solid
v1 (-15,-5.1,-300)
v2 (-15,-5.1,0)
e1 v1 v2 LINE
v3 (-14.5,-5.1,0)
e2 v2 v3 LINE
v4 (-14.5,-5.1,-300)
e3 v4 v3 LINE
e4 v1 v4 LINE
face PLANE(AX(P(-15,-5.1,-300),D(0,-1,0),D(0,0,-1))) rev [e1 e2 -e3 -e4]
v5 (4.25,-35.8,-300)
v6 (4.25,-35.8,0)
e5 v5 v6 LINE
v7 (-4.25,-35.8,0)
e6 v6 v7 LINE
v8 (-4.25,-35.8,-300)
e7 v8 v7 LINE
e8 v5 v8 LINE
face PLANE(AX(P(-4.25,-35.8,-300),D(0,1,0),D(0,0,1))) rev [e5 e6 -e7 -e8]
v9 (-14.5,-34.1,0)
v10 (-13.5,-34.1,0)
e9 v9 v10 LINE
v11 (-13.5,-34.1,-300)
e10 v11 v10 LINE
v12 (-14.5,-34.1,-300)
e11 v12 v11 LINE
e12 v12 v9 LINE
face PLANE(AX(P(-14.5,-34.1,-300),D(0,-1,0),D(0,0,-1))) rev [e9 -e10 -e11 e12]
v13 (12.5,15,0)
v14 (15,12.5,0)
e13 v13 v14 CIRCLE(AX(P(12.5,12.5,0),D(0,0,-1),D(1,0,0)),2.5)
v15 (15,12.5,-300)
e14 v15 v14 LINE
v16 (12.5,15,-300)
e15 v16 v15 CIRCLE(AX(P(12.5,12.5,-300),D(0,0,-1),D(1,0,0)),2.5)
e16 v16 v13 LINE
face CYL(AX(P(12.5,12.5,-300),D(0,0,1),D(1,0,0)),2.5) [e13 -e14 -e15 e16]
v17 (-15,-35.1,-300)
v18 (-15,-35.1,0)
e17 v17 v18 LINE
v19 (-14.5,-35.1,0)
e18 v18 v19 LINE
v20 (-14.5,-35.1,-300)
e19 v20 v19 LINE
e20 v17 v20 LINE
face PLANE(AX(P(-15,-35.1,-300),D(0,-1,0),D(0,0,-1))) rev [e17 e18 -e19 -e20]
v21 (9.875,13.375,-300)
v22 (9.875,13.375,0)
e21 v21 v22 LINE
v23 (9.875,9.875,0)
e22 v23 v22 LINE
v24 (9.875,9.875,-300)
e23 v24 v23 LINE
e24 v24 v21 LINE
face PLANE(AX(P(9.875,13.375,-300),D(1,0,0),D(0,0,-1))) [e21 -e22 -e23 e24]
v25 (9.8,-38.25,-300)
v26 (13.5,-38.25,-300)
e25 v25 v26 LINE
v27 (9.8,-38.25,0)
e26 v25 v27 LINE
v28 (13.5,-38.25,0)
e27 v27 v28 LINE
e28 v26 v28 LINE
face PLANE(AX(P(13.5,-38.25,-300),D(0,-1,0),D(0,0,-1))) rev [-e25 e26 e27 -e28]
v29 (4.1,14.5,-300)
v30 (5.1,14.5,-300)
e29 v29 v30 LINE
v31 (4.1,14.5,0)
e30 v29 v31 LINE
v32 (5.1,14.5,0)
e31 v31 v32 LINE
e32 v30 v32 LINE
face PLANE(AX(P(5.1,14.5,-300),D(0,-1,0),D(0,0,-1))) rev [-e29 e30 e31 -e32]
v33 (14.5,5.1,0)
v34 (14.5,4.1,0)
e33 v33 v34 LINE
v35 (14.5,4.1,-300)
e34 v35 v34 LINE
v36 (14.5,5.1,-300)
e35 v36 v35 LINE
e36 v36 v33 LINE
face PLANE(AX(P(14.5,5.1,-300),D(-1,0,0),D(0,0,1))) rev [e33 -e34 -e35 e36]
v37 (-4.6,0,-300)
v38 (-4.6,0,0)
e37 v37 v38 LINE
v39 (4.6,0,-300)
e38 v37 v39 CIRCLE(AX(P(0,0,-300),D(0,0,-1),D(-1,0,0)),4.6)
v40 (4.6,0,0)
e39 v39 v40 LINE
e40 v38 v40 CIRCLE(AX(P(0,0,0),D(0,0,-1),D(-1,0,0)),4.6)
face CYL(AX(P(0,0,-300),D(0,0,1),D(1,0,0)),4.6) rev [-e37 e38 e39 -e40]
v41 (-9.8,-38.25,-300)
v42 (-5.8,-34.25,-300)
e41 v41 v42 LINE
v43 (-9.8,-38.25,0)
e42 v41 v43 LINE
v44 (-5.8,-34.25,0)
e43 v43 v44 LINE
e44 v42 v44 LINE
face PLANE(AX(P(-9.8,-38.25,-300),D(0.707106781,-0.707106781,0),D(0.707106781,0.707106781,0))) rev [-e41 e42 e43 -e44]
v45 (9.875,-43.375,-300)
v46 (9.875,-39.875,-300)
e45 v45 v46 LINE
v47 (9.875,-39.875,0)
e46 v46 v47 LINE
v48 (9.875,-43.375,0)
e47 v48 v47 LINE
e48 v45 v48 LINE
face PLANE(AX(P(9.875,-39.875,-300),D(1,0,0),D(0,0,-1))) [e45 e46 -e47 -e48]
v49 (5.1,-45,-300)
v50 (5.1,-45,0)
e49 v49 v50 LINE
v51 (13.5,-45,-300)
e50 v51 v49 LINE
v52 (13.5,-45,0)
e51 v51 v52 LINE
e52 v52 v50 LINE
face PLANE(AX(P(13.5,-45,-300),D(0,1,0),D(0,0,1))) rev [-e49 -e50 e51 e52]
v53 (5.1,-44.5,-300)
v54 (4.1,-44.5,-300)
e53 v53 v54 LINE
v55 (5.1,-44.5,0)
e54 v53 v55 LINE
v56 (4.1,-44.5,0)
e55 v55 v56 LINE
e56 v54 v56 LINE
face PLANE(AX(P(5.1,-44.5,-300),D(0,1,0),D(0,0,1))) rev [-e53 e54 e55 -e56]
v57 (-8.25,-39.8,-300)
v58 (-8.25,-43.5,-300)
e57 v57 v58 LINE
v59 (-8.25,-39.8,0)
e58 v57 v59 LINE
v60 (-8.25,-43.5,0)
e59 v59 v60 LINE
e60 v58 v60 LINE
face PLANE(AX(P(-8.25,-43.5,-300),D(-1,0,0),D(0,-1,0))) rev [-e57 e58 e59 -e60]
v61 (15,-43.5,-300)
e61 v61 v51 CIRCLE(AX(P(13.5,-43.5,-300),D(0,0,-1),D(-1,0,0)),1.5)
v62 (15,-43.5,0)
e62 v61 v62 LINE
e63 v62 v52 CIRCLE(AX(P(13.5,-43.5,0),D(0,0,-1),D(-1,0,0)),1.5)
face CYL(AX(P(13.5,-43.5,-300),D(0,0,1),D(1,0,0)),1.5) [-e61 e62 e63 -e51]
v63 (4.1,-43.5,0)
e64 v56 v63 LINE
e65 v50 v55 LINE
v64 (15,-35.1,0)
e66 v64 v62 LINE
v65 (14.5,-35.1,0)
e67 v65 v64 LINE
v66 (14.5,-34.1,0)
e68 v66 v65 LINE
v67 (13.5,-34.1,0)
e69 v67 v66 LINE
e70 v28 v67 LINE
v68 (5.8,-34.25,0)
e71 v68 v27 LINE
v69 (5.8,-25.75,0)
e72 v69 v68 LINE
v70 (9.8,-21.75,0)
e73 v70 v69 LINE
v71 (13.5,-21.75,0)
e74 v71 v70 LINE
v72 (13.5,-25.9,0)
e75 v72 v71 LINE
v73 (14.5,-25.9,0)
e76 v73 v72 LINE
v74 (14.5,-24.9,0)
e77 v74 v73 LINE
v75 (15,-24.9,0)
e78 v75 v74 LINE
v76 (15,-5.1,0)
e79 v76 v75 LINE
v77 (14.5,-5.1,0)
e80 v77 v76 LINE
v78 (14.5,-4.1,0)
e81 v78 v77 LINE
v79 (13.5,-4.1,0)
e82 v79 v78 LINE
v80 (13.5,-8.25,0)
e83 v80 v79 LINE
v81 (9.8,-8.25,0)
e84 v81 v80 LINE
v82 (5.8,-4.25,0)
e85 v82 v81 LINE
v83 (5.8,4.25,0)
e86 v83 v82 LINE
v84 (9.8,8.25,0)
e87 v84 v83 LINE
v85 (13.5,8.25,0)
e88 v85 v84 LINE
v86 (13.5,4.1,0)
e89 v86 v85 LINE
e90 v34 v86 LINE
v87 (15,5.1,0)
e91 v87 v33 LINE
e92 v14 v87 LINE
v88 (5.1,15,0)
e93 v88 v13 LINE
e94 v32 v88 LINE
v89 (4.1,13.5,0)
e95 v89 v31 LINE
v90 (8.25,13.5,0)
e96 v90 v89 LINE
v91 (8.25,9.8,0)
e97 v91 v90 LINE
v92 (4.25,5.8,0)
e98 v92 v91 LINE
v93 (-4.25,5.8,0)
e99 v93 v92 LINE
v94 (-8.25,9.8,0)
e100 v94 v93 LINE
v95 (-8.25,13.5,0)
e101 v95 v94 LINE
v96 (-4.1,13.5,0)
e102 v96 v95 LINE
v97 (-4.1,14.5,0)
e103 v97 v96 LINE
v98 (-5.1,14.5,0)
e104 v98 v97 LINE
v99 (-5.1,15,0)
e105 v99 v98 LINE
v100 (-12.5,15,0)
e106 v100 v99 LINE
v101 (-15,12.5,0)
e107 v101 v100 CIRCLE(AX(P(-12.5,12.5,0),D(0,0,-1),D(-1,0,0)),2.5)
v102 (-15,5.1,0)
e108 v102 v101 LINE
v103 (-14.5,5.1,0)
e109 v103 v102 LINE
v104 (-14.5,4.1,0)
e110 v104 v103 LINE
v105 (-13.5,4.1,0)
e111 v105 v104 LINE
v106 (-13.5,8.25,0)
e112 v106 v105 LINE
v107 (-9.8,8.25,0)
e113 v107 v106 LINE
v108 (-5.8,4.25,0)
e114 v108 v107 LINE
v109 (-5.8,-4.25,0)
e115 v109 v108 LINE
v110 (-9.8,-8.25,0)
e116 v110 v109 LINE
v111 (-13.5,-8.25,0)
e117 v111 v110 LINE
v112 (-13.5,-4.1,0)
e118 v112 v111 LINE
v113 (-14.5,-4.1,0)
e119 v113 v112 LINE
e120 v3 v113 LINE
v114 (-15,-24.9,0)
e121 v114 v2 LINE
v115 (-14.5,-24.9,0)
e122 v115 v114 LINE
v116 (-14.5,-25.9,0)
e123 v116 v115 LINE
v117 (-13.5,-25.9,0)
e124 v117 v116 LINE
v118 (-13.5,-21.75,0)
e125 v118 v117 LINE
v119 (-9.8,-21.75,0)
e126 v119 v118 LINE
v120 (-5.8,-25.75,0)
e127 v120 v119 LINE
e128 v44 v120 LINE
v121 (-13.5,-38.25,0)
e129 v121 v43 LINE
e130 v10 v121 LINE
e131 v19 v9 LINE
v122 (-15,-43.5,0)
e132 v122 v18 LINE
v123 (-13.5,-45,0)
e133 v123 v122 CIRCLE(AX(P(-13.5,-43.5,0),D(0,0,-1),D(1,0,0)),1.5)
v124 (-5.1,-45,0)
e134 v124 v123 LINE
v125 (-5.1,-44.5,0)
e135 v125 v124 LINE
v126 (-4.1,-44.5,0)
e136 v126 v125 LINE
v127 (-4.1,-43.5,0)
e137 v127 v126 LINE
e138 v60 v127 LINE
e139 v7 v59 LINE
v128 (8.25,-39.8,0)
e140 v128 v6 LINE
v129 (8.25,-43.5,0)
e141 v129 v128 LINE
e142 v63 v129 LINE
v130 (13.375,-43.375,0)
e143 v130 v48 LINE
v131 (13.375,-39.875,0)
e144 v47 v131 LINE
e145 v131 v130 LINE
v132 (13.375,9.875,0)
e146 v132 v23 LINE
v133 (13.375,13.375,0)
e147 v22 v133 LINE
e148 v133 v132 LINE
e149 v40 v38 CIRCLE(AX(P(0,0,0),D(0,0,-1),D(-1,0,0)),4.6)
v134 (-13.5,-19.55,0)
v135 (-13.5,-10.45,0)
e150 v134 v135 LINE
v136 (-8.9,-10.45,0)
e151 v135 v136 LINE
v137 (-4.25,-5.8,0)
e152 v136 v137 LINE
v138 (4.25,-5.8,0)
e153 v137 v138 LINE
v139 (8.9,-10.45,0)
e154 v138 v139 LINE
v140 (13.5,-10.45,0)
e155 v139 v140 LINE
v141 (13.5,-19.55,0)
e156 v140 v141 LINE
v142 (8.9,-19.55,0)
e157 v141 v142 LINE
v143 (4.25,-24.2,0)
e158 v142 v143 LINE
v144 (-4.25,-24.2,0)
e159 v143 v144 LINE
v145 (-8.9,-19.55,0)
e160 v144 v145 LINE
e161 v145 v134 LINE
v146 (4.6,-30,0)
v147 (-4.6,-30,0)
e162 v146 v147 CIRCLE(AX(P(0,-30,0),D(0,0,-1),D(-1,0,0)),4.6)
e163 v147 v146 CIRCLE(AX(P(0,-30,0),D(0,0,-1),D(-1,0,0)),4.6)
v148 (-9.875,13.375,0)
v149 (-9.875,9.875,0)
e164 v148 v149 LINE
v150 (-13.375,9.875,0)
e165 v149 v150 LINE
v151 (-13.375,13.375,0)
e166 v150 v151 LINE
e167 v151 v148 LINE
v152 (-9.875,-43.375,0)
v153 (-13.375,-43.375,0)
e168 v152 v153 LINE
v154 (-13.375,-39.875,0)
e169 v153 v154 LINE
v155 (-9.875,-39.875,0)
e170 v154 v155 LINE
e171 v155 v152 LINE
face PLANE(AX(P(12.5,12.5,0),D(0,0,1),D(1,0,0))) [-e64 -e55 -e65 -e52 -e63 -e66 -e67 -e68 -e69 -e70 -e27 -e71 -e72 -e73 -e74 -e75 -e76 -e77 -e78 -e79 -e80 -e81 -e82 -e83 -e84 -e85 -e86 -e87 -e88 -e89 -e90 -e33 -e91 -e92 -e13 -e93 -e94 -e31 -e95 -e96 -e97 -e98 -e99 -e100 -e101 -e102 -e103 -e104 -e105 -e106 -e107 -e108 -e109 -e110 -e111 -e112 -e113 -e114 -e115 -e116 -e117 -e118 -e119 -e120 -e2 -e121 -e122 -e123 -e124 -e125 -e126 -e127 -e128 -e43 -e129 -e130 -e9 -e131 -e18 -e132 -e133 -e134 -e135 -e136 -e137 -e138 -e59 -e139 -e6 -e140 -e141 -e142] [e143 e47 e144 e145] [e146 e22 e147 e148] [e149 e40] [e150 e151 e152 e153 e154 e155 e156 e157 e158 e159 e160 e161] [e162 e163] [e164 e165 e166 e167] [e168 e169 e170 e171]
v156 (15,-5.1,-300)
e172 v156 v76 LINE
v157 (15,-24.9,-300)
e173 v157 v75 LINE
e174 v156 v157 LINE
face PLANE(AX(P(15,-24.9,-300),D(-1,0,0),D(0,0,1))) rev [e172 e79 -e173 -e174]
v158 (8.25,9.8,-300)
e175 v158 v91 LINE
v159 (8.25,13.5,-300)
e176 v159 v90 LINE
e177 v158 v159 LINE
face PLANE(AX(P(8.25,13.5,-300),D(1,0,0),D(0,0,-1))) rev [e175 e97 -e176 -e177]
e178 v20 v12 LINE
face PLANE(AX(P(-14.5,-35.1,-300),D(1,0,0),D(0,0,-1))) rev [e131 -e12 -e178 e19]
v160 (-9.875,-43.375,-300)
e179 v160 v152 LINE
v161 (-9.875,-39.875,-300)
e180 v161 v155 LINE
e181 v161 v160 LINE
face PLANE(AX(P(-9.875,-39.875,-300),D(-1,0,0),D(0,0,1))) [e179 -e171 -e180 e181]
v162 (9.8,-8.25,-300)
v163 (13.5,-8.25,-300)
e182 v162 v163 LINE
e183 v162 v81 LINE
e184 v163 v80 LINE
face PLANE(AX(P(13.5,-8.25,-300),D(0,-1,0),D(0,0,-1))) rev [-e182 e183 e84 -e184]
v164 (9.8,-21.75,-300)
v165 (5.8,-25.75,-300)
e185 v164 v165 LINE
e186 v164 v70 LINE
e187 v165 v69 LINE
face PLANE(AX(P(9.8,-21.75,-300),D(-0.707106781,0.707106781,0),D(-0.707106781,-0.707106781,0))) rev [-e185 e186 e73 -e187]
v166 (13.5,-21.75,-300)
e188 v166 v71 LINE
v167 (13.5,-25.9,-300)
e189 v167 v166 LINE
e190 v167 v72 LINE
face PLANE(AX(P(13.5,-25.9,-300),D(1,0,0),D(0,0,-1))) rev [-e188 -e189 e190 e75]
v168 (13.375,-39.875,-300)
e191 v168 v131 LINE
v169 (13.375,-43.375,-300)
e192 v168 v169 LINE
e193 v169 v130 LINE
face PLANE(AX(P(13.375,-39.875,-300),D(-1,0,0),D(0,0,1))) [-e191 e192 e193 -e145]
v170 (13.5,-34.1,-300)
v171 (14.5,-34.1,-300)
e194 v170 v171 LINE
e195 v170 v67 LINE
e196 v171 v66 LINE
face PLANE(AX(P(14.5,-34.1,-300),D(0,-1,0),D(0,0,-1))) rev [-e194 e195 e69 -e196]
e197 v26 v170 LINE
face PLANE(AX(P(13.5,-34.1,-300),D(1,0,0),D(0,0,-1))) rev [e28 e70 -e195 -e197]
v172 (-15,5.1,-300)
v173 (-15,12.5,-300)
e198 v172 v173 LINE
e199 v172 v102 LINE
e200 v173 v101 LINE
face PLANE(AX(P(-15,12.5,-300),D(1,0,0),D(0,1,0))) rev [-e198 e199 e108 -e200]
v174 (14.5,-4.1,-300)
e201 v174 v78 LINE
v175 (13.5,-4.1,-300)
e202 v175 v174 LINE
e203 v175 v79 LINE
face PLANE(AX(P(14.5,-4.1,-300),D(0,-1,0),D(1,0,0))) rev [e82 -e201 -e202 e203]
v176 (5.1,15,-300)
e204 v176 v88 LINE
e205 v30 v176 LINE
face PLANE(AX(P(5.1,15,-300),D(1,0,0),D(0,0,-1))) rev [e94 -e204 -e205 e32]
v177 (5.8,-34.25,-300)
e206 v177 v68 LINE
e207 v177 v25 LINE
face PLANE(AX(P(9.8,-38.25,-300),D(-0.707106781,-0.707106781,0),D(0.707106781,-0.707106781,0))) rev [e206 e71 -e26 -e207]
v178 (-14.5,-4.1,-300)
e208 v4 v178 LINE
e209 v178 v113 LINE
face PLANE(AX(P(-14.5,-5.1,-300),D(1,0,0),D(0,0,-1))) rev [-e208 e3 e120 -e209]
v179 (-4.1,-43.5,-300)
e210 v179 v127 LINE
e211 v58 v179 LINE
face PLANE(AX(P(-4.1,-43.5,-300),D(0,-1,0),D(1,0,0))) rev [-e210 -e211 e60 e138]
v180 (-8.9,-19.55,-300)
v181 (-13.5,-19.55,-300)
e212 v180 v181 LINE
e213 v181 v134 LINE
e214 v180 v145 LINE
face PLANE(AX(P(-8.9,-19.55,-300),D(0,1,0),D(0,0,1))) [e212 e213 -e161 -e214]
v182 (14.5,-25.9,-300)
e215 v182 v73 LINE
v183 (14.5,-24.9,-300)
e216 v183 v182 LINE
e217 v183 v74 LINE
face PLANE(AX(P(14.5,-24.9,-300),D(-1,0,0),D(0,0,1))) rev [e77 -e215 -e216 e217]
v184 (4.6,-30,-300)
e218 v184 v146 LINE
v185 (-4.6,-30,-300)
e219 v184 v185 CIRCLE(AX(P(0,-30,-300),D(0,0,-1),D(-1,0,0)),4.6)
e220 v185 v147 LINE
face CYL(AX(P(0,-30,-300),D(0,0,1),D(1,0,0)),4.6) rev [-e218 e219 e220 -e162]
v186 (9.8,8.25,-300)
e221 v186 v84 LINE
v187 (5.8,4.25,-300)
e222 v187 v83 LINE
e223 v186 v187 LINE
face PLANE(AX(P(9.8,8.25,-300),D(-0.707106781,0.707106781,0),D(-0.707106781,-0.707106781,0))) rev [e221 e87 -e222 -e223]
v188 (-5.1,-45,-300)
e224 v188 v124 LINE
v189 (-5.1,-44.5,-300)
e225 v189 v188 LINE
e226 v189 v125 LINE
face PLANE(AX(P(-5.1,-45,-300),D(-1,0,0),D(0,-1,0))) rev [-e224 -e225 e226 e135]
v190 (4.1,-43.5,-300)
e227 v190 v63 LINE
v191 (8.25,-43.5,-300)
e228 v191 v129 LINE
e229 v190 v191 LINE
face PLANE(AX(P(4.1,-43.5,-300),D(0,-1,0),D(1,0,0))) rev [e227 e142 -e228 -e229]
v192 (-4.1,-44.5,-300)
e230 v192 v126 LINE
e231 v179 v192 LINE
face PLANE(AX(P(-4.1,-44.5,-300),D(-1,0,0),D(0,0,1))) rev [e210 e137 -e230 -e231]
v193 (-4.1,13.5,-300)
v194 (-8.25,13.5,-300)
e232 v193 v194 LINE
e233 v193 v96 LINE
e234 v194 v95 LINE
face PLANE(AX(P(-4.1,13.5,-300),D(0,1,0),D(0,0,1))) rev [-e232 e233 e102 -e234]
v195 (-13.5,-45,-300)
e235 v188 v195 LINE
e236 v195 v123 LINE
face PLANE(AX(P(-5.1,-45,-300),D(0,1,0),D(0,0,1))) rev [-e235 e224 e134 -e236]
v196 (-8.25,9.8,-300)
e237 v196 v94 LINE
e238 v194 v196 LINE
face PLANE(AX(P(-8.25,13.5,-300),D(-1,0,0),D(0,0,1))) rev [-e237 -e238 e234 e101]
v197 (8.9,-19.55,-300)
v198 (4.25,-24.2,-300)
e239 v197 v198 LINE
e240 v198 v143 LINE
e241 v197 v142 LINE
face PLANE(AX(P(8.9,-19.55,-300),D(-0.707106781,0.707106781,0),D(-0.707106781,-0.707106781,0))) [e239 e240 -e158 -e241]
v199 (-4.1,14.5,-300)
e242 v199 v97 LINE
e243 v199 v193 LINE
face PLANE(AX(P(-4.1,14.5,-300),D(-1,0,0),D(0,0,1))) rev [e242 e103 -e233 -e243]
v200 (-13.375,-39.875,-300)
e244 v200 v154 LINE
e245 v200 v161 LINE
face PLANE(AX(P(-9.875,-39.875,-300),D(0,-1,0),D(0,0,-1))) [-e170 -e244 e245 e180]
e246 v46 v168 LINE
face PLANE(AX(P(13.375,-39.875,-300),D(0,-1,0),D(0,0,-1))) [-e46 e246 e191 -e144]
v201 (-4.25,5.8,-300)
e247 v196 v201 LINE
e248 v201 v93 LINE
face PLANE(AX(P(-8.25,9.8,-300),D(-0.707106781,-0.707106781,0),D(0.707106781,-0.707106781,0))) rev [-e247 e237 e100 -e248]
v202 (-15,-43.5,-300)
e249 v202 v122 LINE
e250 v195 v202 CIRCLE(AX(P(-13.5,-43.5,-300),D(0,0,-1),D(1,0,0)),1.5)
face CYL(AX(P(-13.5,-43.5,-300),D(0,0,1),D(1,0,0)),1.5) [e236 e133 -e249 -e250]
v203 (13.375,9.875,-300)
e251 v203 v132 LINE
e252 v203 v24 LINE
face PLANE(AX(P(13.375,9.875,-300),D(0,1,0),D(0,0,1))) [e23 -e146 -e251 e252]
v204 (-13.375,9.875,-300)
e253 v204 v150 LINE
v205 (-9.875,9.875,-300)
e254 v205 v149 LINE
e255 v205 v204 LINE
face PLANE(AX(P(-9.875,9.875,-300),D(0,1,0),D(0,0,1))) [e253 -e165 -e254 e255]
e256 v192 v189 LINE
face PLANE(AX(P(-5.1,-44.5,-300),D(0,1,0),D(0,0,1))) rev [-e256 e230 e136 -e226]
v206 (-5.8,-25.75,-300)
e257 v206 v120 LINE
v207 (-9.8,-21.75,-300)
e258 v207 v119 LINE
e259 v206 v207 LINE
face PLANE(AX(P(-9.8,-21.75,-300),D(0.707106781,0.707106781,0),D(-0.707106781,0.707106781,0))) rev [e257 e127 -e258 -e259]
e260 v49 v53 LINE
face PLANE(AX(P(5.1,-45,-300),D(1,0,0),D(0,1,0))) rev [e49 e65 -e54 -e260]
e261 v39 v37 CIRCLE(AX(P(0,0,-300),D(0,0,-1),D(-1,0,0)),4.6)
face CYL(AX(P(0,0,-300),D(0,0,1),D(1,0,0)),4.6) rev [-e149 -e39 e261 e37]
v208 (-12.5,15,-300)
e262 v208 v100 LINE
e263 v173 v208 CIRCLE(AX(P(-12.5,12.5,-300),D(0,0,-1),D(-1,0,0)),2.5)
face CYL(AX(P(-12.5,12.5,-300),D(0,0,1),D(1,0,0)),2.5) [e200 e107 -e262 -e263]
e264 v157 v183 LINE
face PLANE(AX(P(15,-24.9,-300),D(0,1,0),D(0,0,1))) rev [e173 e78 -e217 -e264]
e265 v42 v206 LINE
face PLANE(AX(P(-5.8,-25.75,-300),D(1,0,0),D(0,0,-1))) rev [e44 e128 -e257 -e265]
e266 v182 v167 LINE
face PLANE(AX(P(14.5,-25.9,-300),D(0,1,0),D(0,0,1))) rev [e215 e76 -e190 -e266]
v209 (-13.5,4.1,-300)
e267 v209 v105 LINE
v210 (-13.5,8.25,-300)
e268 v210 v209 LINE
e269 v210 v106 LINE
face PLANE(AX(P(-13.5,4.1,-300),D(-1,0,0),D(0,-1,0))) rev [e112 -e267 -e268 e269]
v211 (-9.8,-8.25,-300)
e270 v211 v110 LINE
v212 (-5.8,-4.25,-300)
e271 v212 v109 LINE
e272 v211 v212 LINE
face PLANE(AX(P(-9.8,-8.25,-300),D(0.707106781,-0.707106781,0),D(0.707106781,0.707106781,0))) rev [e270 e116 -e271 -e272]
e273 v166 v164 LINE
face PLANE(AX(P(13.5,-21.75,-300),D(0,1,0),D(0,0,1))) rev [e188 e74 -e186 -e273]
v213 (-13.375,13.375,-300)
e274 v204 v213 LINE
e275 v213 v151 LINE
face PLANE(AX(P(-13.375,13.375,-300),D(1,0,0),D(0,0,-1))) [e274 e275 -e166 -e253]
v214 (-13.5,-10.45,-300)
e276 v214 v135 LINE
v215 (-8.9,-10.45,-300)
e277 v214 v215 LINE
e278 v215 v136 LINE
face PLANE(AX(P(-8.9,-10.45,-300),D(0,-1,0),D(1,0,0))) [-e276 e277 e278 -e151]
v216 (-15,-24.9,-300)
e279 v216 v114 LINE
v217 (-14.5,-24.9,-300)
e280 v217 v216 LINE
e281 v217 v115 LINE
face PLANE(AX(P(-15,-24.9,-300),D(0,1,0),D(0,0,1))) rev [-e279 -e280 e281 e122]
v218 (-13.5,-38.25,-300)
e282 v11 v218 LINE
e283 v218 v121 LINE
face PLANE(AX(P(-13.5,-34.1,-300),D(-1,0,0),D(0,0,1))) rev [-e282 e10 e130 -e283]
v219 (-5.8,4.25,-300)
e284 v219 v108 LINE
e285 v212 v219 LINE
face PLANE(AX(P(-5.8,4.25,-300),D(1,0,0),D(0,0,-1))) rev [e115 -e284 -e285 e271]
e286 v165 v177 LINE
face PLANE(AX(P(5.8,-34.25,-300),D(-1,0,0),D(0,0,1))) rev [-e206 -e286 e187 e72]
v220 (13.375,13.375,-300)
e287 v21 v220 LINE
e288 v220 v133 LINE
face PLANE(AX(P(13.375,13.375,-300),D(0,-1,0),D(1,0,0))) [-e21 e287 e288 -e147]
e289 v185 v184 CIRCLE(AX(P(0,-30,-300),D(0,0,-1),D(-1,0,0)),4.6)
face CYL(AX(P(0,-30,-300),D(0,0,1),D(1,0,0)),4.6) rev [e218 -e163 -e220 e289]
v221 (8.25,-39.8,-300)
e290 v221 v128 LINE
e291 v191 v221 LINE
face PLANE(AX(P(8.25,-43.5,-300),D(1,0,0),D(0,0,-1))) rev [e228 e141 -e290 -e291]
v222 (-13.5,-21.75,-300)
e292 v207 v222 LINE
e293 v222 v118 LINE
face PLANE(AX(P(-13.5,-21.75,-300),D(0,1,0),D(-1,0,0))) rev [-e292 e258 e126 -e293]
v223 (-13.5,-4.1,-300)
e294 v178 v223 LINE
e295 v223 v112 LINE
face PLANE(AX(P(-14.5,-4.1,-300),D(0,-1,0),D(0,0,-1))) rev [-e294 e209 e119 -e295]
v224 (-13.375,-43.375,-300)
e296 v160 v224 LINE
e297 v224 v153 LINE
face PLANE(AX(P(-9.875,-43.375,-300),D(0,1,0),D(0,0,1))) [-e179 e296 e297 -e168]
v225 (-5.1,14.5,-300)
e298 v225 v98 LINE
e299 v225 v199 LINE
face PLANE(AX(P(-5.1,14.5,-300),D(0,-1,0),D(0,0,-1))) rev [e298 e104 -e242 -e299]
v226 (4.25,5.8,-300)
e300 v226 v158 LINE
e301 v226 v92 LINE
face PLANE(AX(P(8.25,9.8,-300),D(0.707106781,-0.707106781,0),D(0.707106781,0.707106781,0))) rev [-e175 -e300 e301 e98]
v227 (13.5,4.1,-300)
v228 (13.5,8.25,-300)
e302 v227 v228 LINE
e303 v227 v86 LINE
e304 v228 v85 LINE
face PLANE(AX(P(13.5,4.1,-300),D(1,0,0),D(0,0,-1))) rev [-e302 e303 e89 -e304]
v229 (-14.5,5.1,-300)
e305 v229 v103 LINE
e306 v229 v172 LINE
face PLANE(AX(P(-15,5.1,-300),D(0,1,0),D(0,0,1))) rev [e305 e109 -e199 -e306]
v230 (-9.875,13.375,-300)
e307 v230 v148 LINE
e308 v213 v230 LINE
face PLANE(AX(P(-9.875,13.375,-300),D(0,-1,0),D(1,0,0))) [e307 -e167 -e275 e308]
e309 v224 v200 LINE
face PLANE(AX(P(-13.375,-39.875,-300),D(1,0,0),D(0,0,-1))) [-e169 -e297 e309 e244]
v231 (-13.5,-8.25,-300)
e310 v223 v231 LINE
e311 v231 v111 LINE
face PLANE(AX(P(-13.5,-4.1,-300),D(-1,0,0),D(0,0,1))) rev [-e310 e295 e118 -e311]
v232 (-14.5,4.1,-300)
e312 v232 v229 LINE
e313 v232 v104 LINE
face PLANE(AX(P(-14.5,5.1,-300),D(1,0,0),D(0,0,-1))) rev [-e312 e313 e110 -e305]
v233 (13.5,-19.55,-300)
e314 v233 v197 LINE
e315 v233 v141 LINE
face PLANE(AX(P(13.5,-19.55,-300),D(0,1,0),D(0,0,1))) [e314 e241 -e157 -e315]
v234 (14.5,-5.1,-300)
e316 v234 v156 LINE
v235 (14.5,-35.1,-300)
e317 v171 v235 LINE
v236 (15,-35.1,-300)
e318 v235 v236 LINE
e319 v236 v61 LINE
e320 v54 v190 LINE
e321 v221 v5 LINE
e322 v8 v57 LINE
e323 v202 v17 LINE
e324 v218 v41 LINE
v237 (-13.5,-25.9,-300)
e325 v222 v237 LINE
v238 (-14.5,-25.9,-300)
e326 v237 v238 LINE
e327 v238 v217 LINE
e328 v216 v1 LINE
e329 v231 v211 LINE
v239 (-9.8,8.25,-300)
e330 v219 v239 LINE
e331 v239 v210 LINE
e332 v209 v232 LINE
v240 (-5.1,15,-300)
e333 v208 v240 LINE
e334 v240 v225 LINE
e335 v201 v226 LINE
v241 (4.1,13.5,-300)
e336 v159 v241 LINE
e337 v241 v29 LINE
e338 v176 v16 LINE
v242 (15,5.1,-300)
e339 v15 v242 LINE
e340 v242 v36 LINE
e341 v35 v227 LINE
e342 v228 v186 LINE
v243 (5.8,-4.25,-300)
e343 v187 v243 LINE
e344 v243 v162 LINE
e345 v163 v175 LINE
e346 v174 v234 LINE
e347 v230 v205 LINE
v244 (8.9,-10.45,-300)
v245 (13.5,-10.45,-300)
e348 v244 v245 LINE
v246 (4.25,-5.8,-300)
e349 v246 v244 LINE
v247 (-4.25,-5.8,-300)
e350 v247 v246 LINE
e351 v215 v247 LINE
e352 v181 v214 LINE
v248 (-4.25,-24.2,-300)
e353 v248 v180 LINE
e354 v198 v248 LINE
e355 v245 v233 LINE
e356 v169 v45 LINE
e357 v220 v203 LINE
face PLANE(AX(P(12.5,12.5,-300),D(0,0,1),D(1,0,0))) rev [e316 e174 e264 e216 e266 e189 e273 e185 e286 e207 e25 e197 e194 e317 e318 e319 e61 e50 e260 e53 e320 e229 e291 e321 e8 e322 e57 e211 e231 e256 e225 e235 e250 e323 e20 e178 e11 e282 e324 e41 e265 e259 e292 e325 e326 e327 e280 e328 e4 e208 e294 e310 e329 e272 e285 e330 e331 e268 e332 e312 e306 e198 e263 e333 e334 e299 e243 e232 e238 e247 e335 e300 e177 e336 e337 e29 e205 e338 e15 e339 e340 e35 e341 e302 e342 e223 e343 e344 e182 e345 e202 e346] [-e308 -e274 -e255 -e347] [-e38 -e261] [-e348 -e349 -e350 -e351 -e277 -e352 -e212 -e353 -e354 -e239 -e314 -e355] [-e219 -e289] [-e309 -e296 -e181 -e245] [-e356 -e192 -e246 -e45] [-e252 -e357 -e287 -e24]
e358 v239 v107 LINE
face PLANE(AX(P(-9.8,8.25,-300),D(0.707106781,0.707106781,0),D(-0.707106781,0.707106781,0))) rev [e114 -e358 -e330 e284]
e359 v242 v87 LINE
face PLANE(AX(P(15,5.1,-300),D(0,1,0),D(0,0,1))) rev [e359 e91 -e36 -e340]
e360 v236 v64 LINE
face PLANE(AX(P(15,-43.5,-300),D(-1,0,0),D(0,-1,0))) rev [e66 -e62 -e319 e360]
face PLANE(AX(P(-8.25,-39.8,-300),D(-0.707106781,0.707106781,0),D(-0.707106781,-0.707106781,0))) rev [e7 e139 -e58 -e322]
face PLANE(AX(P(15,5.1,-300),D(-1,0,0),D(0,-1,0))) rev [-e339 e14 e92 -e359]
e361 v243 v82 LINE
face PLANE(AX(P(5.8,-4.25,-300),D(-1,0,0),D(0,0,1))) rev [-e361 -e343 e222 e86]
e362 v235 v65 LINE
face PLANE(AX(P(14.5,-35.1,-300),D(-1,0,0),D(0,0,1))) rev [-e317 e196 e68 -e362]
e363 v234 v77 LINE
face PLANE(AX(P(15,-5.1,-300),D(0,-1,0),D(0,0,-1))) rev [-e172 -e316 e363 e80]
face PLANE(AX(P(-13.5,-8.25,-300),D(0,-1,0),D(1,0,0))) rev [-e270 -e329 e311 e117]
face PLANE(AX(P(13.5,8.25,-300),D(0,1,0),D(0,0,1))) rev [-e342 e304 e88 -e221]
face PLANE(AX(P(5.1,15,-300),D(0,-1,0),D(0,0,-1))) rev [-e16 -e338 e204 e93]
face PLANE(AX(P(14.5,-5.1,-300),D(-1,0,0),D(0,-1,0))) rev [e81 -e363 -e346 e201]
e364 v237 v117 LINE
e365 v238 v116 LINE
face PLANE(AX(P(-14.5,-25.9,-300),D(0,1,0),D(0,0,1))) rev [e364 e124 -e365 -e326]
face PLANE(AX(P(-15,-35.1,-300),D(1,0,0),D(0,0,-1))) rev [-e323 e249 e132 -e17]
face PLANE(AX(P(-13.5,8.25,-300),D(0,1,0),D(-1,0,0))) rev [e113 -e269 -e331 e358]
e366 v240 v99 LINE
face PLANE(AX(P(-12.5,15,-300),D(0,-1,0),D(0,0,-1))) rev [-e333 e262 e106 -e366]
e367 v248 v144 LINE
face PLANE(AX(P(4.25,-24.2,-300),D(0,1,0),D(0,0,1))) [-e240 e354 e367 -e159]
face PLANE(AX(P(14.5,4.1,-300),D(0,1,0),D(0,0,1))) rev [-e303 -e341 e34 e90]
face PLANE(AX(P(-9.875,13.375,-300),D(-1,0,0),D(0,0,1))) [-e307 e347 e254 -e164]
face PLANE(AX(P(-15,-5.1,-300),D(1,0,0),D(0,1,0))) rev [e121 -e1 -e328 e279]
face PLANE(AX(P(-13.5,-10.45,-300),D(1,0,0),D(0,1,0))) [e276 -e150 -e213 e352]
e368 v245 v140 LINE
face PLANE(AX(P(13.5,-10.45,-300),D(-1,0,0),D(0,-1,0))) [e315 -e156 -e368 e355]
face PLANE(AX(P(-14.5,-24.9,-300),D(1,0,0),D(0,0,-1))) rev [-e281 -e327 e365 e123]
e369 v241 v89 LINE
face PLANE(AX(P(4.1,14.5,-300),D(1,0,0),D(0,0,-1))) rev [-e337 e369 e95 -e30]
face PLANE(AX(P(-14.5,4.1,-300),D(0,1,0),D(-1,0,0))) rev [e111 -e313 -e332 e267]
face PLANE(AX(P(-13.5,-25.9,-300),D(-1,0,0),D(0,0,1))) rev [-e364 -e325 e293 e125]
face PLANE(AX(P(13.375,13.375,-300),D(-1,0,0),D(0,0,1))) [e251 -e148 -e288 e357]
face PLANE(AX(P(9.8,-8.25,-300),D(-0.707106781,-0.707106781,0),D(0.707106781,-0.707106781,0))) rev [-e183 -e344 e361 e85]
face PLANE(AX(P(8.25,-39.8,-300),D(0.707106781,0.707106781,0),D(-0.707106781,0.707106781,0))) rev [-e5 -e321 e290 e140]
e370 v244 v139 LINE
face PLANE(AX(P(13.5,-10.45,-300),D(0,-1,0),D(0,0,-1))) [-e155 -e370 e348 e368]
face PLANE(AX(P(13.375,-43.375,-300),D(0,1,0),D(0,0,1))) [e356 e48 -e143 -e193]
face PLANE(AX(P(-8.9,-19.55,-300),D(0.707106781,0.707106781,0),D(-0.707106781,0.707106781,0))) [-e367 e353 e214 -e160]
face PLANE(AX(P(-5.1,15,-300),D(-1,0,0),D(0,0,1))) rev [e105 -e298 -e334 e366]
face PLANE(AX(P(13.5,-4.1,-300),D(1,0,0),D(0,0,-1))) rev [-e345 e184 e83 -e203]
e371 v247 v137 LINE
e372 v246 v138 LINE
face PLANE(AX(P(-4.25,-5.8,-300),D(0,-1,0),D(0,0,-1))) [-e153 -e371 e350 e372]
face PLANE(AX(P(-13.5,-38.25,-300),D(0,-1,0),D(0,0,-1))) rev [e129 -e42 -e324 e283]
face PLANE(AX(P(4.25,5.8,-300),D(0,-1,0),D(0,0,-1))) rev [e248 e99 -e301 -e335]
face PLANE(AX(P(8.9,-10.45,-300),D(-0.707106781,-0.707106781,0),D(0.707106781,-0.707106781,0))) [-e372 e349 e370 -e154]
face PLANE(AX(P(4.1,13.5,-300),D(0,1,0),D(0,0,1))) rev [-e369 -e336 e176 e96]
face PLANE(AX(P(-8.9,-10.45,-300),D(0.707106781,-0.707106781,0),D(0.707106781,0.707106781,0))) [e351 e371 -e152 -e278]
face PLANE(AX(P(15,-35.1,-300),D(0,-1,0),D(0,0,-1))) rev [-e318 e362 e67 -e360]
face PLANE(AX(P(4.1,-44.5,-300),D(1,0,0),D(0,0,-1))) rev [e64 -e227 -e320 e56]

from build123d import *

# Parameters (mm, degrees)
SKETCH1_R                 = 4.6
SKETCH1_W                 = 3.5
SKETCH1_H                 = 3.5
F_30_X_60L_X_R2_5_1_DEPTH = 300


with BuildPart() as part:
    # Sketch1 → 铝型材 30 X 60L X R2.5(1) (new body)
    with BuildSketch(Plane(origin=(0, 0, 0), x_dir=(-1, 0, 0), z_dir=(0, 0, -1))):
        with BuildLine():
            Line((-5.1, 15), (-5.1, 14.5))
            Line((-5.1, 14.5), (-4.1, 14.5))
            Line((-4.1, 14.5), (-4.1, 13.5))
            Line((-4.1, 13.5), (-8.25, 13.5))
            Line((-8.25, 13.5), (-8.25, 9.8))
            Line((-8.25, 9.8), (-4.25, 5.8))
            Line((-4.25, 5.8), (4.25, 5.8))
            Line((4.25, 5.8), (8.25, 9.8))
            Line((8.25, 9.8), (8.25, 13.5))
            Line((8.25, 13.5), (4.1, 13.5))
            Line((4.1, 13.5), (4.1, 14.5))
            Line((4.1, 14.5), (5.1, 14.5))
            Line((5.1, 14.5), (5.1, 15))
            Line((5.1, 15), (12.5, 15))
            ThreePointArc((12.5, 15), (14.267766953, 14.267766953), (15, 12.5))
            Line((15, 12.5), (15, 5.1))
            Line((15, 5.1), (14.5, 5.1))
            Line((14.5, 5.1), (14.5, 4.1))
            Line((14.5, 4.1), (13.5, 4.1))
            Line((13.5, 4.1), (13.5, 8.25))
            Line((13.5, 8.25), (9.8, 8.25))
            Line((9.8, 8.25), (5.8, 4.25))
            Line((5.8, 4.25), (5.8, -4.25))
            Line((5.8, -4.25), (9.8, -8.25))
            Line((9.8, -8.25), (13.5, -8.25))
            Line((13.5, -8.25), (13.5, -4.1))
            Line((13.5, -4.1), (14.5, -4.1))
            Line((14.5, -4.1), (14.5, -5.1))
            Line((14.5, -5.1), (15, -5.1))
            Line((15, -5.1), (15, -24.9))
            Line((15, -24.9), (14.5, -24.9))
            Line((14.5, -24.9), (14.5, -25.9))
            Line((14.5, -25.9), (13.5, -25.9))
            Line((13.5, -25.9), (13.5, -21.75))
            Line((13.5, -21.75), (9.8, -21.75))
            Line((9.8, -21.75), (5.8, -25.75))
            Line((5.8, -25.75), (5.8, -34.25))
            Line((5.8, -34.25), (9.8, -38.25))
            Line((9.8, -38.25), (13.5, -38.25))
            Line((13.5, -38.25), (13.5, -34.1))
            Line((13.5, -34.1), (14.5, -34.1))
            Line((14.5, -34.1), (14.5, -35.1))
            Line((14.5, -35.1), (15, -35.1))
            Line((15, -35.1), (15, -43.5))
            ThreePointArc((15, -43.5), (14.560660172, -44.560660172), (13.5, -45))
            Line((13.5, -45), (5.1, -45))
            Line((5.1, -45), (5.1, -44.5))
            Line((5.1, -44.5), (4.1, -44.5))
            Line((4.1, -44.5), (4.1, -43.5))
            Line((4.1, -43.5), (8.25, -43.5))
            Line((8.25, -43.5), (8.25, -39.8))
            Line((8.25, -39.8), (4.25, -35.8))
            Line((4.25, -35.8), (-4.25, -35.8))
            Line((-4.25, -35.8), (-8.25, -39.8))
            Line((-8.25, -39.8), (-8.25, -43.5))
            Line((-8.25, -43.5), (-4.1, -43.5))
            Line((-4.1, -43.5), (-4.1, -44.5))
            Line((-4.1, -44.5), (-5.1, -44.5))
            Line((-5.1, -44.5), (-5.1, -45))
            Line((-5.1, -45), (-13.5, -45))
            ThreePointArc((-13.5, -45), (-14.560660172, -44.560660172), (-15, -43.5))
            Line((-15, -43.5), (-15, -35.1))
            Line((-15, -35.1), (-14.5, -35.1))
            Line((-14.5, -35.1), (-14.5, -34.1))
            Line((-14.5, -34.1), (-13.5, -34.1))
            Line((-13.5, -34.1), (-13.5, -38.25))
            Line((-13.5, -38.25), (-9.8, -38.25))
            Line((-9.8, -38.25), (-5.8, -34.25))
            Line((-5.8, -34.25), (-5.8, -25.75))
            Line((-5.8, -25.75), (-9.8, -21.75))
            Line((-9.8, -21.75), (-13.5, -21.75))
            Line((-13.5, -21.75), (-13.5, -25.9))
            Line((-13.5, -25.9), (-14.5, -25.9))
            Line((-14.5, -25.9), (-14.5, -24.9))
            Line((-14.5, -24.9), (-15, -24.9))
            Line((-15, -24.9), (-15, -5.1))
            Line((-15, -5.1), (-14.5, -5.1))
            Line((-14.5, -5.1), (-14.5, -4.1))
            Line((-14.5, -4.1), (-13.5, -4.1))
            Line((-13.5, -4.1), (-13.5, -8.25))
            Line((-13.5, -8.25), (-9.8, -8.25))
            Line((-9.8, -8.25), (-5.8, -4.25))
            Line((-5.8, -4.25), (-5.8, 4.25))
            Line((-5.8, 4.25), (-9.8, 8.25))
            Line((-9.8, 8.25), (-13.5, 8.25))
            Line((-13.5, 8.25), (-13.5, 4.1))
            Line((-13.5, 4.1), (-14.5, 4.1))
            Line((-14.5, 4.1), (-14.5, 5.1))
            Line((-14.5, 5.1), (-15, 5.1))
            Line((-15, 5.1), (-15, 12.5))
            ThreePointArc((-15, 12.5), (-14.267766953, 14.267766953), (-12.5, 15))
            Line((-12.5, 15), (-5.1, 15))
        make_face()
        Circle(SKETCH1_R, mode=Mode.SUBTRACT)
        with Locations((0, -30)):
            Circle(SKETCH1_R, mode=Mode.SUBTRACT)
        Polygon((8.9, -10.45), (4.25, -5.8), (-4.25, -5.8), (-8.9, -10.45), (-13.5, -10.45), (-13.5, -19.55), (-8.9, -19.55), (-4.25, -24.2), (4.25, -24.2), (8.9, -19.55), (13.5, -19.55), (13.5, -10.45), align=None, mode=Mode.SUBTRACT)
        with Locations((-11.625, 11.625)):
            Rectangle(SKETCH1_W, SKETCH1_H, mode=Mode.SUBTRACT)
        with Locations((11.625, 11.625)):
            Rectangle(SKETCH1_W, SKETCH1_H, mode=Mode.SUBTRACT)
        with Locations((-11.625, -41.625)):
            Rectangle(SKETCH1_W, SKETCH1_H, mode=Mode.SUBTRACT)
        with Locations((11.625, -41.625)):
            Rectangle(SKETCH1_W, SKETCH1_H, mode=Mode.SUBTRACT)
    extrude(amount=F_30_X_60L_X_R2_5_1_DEPTH)


solid = part.part
